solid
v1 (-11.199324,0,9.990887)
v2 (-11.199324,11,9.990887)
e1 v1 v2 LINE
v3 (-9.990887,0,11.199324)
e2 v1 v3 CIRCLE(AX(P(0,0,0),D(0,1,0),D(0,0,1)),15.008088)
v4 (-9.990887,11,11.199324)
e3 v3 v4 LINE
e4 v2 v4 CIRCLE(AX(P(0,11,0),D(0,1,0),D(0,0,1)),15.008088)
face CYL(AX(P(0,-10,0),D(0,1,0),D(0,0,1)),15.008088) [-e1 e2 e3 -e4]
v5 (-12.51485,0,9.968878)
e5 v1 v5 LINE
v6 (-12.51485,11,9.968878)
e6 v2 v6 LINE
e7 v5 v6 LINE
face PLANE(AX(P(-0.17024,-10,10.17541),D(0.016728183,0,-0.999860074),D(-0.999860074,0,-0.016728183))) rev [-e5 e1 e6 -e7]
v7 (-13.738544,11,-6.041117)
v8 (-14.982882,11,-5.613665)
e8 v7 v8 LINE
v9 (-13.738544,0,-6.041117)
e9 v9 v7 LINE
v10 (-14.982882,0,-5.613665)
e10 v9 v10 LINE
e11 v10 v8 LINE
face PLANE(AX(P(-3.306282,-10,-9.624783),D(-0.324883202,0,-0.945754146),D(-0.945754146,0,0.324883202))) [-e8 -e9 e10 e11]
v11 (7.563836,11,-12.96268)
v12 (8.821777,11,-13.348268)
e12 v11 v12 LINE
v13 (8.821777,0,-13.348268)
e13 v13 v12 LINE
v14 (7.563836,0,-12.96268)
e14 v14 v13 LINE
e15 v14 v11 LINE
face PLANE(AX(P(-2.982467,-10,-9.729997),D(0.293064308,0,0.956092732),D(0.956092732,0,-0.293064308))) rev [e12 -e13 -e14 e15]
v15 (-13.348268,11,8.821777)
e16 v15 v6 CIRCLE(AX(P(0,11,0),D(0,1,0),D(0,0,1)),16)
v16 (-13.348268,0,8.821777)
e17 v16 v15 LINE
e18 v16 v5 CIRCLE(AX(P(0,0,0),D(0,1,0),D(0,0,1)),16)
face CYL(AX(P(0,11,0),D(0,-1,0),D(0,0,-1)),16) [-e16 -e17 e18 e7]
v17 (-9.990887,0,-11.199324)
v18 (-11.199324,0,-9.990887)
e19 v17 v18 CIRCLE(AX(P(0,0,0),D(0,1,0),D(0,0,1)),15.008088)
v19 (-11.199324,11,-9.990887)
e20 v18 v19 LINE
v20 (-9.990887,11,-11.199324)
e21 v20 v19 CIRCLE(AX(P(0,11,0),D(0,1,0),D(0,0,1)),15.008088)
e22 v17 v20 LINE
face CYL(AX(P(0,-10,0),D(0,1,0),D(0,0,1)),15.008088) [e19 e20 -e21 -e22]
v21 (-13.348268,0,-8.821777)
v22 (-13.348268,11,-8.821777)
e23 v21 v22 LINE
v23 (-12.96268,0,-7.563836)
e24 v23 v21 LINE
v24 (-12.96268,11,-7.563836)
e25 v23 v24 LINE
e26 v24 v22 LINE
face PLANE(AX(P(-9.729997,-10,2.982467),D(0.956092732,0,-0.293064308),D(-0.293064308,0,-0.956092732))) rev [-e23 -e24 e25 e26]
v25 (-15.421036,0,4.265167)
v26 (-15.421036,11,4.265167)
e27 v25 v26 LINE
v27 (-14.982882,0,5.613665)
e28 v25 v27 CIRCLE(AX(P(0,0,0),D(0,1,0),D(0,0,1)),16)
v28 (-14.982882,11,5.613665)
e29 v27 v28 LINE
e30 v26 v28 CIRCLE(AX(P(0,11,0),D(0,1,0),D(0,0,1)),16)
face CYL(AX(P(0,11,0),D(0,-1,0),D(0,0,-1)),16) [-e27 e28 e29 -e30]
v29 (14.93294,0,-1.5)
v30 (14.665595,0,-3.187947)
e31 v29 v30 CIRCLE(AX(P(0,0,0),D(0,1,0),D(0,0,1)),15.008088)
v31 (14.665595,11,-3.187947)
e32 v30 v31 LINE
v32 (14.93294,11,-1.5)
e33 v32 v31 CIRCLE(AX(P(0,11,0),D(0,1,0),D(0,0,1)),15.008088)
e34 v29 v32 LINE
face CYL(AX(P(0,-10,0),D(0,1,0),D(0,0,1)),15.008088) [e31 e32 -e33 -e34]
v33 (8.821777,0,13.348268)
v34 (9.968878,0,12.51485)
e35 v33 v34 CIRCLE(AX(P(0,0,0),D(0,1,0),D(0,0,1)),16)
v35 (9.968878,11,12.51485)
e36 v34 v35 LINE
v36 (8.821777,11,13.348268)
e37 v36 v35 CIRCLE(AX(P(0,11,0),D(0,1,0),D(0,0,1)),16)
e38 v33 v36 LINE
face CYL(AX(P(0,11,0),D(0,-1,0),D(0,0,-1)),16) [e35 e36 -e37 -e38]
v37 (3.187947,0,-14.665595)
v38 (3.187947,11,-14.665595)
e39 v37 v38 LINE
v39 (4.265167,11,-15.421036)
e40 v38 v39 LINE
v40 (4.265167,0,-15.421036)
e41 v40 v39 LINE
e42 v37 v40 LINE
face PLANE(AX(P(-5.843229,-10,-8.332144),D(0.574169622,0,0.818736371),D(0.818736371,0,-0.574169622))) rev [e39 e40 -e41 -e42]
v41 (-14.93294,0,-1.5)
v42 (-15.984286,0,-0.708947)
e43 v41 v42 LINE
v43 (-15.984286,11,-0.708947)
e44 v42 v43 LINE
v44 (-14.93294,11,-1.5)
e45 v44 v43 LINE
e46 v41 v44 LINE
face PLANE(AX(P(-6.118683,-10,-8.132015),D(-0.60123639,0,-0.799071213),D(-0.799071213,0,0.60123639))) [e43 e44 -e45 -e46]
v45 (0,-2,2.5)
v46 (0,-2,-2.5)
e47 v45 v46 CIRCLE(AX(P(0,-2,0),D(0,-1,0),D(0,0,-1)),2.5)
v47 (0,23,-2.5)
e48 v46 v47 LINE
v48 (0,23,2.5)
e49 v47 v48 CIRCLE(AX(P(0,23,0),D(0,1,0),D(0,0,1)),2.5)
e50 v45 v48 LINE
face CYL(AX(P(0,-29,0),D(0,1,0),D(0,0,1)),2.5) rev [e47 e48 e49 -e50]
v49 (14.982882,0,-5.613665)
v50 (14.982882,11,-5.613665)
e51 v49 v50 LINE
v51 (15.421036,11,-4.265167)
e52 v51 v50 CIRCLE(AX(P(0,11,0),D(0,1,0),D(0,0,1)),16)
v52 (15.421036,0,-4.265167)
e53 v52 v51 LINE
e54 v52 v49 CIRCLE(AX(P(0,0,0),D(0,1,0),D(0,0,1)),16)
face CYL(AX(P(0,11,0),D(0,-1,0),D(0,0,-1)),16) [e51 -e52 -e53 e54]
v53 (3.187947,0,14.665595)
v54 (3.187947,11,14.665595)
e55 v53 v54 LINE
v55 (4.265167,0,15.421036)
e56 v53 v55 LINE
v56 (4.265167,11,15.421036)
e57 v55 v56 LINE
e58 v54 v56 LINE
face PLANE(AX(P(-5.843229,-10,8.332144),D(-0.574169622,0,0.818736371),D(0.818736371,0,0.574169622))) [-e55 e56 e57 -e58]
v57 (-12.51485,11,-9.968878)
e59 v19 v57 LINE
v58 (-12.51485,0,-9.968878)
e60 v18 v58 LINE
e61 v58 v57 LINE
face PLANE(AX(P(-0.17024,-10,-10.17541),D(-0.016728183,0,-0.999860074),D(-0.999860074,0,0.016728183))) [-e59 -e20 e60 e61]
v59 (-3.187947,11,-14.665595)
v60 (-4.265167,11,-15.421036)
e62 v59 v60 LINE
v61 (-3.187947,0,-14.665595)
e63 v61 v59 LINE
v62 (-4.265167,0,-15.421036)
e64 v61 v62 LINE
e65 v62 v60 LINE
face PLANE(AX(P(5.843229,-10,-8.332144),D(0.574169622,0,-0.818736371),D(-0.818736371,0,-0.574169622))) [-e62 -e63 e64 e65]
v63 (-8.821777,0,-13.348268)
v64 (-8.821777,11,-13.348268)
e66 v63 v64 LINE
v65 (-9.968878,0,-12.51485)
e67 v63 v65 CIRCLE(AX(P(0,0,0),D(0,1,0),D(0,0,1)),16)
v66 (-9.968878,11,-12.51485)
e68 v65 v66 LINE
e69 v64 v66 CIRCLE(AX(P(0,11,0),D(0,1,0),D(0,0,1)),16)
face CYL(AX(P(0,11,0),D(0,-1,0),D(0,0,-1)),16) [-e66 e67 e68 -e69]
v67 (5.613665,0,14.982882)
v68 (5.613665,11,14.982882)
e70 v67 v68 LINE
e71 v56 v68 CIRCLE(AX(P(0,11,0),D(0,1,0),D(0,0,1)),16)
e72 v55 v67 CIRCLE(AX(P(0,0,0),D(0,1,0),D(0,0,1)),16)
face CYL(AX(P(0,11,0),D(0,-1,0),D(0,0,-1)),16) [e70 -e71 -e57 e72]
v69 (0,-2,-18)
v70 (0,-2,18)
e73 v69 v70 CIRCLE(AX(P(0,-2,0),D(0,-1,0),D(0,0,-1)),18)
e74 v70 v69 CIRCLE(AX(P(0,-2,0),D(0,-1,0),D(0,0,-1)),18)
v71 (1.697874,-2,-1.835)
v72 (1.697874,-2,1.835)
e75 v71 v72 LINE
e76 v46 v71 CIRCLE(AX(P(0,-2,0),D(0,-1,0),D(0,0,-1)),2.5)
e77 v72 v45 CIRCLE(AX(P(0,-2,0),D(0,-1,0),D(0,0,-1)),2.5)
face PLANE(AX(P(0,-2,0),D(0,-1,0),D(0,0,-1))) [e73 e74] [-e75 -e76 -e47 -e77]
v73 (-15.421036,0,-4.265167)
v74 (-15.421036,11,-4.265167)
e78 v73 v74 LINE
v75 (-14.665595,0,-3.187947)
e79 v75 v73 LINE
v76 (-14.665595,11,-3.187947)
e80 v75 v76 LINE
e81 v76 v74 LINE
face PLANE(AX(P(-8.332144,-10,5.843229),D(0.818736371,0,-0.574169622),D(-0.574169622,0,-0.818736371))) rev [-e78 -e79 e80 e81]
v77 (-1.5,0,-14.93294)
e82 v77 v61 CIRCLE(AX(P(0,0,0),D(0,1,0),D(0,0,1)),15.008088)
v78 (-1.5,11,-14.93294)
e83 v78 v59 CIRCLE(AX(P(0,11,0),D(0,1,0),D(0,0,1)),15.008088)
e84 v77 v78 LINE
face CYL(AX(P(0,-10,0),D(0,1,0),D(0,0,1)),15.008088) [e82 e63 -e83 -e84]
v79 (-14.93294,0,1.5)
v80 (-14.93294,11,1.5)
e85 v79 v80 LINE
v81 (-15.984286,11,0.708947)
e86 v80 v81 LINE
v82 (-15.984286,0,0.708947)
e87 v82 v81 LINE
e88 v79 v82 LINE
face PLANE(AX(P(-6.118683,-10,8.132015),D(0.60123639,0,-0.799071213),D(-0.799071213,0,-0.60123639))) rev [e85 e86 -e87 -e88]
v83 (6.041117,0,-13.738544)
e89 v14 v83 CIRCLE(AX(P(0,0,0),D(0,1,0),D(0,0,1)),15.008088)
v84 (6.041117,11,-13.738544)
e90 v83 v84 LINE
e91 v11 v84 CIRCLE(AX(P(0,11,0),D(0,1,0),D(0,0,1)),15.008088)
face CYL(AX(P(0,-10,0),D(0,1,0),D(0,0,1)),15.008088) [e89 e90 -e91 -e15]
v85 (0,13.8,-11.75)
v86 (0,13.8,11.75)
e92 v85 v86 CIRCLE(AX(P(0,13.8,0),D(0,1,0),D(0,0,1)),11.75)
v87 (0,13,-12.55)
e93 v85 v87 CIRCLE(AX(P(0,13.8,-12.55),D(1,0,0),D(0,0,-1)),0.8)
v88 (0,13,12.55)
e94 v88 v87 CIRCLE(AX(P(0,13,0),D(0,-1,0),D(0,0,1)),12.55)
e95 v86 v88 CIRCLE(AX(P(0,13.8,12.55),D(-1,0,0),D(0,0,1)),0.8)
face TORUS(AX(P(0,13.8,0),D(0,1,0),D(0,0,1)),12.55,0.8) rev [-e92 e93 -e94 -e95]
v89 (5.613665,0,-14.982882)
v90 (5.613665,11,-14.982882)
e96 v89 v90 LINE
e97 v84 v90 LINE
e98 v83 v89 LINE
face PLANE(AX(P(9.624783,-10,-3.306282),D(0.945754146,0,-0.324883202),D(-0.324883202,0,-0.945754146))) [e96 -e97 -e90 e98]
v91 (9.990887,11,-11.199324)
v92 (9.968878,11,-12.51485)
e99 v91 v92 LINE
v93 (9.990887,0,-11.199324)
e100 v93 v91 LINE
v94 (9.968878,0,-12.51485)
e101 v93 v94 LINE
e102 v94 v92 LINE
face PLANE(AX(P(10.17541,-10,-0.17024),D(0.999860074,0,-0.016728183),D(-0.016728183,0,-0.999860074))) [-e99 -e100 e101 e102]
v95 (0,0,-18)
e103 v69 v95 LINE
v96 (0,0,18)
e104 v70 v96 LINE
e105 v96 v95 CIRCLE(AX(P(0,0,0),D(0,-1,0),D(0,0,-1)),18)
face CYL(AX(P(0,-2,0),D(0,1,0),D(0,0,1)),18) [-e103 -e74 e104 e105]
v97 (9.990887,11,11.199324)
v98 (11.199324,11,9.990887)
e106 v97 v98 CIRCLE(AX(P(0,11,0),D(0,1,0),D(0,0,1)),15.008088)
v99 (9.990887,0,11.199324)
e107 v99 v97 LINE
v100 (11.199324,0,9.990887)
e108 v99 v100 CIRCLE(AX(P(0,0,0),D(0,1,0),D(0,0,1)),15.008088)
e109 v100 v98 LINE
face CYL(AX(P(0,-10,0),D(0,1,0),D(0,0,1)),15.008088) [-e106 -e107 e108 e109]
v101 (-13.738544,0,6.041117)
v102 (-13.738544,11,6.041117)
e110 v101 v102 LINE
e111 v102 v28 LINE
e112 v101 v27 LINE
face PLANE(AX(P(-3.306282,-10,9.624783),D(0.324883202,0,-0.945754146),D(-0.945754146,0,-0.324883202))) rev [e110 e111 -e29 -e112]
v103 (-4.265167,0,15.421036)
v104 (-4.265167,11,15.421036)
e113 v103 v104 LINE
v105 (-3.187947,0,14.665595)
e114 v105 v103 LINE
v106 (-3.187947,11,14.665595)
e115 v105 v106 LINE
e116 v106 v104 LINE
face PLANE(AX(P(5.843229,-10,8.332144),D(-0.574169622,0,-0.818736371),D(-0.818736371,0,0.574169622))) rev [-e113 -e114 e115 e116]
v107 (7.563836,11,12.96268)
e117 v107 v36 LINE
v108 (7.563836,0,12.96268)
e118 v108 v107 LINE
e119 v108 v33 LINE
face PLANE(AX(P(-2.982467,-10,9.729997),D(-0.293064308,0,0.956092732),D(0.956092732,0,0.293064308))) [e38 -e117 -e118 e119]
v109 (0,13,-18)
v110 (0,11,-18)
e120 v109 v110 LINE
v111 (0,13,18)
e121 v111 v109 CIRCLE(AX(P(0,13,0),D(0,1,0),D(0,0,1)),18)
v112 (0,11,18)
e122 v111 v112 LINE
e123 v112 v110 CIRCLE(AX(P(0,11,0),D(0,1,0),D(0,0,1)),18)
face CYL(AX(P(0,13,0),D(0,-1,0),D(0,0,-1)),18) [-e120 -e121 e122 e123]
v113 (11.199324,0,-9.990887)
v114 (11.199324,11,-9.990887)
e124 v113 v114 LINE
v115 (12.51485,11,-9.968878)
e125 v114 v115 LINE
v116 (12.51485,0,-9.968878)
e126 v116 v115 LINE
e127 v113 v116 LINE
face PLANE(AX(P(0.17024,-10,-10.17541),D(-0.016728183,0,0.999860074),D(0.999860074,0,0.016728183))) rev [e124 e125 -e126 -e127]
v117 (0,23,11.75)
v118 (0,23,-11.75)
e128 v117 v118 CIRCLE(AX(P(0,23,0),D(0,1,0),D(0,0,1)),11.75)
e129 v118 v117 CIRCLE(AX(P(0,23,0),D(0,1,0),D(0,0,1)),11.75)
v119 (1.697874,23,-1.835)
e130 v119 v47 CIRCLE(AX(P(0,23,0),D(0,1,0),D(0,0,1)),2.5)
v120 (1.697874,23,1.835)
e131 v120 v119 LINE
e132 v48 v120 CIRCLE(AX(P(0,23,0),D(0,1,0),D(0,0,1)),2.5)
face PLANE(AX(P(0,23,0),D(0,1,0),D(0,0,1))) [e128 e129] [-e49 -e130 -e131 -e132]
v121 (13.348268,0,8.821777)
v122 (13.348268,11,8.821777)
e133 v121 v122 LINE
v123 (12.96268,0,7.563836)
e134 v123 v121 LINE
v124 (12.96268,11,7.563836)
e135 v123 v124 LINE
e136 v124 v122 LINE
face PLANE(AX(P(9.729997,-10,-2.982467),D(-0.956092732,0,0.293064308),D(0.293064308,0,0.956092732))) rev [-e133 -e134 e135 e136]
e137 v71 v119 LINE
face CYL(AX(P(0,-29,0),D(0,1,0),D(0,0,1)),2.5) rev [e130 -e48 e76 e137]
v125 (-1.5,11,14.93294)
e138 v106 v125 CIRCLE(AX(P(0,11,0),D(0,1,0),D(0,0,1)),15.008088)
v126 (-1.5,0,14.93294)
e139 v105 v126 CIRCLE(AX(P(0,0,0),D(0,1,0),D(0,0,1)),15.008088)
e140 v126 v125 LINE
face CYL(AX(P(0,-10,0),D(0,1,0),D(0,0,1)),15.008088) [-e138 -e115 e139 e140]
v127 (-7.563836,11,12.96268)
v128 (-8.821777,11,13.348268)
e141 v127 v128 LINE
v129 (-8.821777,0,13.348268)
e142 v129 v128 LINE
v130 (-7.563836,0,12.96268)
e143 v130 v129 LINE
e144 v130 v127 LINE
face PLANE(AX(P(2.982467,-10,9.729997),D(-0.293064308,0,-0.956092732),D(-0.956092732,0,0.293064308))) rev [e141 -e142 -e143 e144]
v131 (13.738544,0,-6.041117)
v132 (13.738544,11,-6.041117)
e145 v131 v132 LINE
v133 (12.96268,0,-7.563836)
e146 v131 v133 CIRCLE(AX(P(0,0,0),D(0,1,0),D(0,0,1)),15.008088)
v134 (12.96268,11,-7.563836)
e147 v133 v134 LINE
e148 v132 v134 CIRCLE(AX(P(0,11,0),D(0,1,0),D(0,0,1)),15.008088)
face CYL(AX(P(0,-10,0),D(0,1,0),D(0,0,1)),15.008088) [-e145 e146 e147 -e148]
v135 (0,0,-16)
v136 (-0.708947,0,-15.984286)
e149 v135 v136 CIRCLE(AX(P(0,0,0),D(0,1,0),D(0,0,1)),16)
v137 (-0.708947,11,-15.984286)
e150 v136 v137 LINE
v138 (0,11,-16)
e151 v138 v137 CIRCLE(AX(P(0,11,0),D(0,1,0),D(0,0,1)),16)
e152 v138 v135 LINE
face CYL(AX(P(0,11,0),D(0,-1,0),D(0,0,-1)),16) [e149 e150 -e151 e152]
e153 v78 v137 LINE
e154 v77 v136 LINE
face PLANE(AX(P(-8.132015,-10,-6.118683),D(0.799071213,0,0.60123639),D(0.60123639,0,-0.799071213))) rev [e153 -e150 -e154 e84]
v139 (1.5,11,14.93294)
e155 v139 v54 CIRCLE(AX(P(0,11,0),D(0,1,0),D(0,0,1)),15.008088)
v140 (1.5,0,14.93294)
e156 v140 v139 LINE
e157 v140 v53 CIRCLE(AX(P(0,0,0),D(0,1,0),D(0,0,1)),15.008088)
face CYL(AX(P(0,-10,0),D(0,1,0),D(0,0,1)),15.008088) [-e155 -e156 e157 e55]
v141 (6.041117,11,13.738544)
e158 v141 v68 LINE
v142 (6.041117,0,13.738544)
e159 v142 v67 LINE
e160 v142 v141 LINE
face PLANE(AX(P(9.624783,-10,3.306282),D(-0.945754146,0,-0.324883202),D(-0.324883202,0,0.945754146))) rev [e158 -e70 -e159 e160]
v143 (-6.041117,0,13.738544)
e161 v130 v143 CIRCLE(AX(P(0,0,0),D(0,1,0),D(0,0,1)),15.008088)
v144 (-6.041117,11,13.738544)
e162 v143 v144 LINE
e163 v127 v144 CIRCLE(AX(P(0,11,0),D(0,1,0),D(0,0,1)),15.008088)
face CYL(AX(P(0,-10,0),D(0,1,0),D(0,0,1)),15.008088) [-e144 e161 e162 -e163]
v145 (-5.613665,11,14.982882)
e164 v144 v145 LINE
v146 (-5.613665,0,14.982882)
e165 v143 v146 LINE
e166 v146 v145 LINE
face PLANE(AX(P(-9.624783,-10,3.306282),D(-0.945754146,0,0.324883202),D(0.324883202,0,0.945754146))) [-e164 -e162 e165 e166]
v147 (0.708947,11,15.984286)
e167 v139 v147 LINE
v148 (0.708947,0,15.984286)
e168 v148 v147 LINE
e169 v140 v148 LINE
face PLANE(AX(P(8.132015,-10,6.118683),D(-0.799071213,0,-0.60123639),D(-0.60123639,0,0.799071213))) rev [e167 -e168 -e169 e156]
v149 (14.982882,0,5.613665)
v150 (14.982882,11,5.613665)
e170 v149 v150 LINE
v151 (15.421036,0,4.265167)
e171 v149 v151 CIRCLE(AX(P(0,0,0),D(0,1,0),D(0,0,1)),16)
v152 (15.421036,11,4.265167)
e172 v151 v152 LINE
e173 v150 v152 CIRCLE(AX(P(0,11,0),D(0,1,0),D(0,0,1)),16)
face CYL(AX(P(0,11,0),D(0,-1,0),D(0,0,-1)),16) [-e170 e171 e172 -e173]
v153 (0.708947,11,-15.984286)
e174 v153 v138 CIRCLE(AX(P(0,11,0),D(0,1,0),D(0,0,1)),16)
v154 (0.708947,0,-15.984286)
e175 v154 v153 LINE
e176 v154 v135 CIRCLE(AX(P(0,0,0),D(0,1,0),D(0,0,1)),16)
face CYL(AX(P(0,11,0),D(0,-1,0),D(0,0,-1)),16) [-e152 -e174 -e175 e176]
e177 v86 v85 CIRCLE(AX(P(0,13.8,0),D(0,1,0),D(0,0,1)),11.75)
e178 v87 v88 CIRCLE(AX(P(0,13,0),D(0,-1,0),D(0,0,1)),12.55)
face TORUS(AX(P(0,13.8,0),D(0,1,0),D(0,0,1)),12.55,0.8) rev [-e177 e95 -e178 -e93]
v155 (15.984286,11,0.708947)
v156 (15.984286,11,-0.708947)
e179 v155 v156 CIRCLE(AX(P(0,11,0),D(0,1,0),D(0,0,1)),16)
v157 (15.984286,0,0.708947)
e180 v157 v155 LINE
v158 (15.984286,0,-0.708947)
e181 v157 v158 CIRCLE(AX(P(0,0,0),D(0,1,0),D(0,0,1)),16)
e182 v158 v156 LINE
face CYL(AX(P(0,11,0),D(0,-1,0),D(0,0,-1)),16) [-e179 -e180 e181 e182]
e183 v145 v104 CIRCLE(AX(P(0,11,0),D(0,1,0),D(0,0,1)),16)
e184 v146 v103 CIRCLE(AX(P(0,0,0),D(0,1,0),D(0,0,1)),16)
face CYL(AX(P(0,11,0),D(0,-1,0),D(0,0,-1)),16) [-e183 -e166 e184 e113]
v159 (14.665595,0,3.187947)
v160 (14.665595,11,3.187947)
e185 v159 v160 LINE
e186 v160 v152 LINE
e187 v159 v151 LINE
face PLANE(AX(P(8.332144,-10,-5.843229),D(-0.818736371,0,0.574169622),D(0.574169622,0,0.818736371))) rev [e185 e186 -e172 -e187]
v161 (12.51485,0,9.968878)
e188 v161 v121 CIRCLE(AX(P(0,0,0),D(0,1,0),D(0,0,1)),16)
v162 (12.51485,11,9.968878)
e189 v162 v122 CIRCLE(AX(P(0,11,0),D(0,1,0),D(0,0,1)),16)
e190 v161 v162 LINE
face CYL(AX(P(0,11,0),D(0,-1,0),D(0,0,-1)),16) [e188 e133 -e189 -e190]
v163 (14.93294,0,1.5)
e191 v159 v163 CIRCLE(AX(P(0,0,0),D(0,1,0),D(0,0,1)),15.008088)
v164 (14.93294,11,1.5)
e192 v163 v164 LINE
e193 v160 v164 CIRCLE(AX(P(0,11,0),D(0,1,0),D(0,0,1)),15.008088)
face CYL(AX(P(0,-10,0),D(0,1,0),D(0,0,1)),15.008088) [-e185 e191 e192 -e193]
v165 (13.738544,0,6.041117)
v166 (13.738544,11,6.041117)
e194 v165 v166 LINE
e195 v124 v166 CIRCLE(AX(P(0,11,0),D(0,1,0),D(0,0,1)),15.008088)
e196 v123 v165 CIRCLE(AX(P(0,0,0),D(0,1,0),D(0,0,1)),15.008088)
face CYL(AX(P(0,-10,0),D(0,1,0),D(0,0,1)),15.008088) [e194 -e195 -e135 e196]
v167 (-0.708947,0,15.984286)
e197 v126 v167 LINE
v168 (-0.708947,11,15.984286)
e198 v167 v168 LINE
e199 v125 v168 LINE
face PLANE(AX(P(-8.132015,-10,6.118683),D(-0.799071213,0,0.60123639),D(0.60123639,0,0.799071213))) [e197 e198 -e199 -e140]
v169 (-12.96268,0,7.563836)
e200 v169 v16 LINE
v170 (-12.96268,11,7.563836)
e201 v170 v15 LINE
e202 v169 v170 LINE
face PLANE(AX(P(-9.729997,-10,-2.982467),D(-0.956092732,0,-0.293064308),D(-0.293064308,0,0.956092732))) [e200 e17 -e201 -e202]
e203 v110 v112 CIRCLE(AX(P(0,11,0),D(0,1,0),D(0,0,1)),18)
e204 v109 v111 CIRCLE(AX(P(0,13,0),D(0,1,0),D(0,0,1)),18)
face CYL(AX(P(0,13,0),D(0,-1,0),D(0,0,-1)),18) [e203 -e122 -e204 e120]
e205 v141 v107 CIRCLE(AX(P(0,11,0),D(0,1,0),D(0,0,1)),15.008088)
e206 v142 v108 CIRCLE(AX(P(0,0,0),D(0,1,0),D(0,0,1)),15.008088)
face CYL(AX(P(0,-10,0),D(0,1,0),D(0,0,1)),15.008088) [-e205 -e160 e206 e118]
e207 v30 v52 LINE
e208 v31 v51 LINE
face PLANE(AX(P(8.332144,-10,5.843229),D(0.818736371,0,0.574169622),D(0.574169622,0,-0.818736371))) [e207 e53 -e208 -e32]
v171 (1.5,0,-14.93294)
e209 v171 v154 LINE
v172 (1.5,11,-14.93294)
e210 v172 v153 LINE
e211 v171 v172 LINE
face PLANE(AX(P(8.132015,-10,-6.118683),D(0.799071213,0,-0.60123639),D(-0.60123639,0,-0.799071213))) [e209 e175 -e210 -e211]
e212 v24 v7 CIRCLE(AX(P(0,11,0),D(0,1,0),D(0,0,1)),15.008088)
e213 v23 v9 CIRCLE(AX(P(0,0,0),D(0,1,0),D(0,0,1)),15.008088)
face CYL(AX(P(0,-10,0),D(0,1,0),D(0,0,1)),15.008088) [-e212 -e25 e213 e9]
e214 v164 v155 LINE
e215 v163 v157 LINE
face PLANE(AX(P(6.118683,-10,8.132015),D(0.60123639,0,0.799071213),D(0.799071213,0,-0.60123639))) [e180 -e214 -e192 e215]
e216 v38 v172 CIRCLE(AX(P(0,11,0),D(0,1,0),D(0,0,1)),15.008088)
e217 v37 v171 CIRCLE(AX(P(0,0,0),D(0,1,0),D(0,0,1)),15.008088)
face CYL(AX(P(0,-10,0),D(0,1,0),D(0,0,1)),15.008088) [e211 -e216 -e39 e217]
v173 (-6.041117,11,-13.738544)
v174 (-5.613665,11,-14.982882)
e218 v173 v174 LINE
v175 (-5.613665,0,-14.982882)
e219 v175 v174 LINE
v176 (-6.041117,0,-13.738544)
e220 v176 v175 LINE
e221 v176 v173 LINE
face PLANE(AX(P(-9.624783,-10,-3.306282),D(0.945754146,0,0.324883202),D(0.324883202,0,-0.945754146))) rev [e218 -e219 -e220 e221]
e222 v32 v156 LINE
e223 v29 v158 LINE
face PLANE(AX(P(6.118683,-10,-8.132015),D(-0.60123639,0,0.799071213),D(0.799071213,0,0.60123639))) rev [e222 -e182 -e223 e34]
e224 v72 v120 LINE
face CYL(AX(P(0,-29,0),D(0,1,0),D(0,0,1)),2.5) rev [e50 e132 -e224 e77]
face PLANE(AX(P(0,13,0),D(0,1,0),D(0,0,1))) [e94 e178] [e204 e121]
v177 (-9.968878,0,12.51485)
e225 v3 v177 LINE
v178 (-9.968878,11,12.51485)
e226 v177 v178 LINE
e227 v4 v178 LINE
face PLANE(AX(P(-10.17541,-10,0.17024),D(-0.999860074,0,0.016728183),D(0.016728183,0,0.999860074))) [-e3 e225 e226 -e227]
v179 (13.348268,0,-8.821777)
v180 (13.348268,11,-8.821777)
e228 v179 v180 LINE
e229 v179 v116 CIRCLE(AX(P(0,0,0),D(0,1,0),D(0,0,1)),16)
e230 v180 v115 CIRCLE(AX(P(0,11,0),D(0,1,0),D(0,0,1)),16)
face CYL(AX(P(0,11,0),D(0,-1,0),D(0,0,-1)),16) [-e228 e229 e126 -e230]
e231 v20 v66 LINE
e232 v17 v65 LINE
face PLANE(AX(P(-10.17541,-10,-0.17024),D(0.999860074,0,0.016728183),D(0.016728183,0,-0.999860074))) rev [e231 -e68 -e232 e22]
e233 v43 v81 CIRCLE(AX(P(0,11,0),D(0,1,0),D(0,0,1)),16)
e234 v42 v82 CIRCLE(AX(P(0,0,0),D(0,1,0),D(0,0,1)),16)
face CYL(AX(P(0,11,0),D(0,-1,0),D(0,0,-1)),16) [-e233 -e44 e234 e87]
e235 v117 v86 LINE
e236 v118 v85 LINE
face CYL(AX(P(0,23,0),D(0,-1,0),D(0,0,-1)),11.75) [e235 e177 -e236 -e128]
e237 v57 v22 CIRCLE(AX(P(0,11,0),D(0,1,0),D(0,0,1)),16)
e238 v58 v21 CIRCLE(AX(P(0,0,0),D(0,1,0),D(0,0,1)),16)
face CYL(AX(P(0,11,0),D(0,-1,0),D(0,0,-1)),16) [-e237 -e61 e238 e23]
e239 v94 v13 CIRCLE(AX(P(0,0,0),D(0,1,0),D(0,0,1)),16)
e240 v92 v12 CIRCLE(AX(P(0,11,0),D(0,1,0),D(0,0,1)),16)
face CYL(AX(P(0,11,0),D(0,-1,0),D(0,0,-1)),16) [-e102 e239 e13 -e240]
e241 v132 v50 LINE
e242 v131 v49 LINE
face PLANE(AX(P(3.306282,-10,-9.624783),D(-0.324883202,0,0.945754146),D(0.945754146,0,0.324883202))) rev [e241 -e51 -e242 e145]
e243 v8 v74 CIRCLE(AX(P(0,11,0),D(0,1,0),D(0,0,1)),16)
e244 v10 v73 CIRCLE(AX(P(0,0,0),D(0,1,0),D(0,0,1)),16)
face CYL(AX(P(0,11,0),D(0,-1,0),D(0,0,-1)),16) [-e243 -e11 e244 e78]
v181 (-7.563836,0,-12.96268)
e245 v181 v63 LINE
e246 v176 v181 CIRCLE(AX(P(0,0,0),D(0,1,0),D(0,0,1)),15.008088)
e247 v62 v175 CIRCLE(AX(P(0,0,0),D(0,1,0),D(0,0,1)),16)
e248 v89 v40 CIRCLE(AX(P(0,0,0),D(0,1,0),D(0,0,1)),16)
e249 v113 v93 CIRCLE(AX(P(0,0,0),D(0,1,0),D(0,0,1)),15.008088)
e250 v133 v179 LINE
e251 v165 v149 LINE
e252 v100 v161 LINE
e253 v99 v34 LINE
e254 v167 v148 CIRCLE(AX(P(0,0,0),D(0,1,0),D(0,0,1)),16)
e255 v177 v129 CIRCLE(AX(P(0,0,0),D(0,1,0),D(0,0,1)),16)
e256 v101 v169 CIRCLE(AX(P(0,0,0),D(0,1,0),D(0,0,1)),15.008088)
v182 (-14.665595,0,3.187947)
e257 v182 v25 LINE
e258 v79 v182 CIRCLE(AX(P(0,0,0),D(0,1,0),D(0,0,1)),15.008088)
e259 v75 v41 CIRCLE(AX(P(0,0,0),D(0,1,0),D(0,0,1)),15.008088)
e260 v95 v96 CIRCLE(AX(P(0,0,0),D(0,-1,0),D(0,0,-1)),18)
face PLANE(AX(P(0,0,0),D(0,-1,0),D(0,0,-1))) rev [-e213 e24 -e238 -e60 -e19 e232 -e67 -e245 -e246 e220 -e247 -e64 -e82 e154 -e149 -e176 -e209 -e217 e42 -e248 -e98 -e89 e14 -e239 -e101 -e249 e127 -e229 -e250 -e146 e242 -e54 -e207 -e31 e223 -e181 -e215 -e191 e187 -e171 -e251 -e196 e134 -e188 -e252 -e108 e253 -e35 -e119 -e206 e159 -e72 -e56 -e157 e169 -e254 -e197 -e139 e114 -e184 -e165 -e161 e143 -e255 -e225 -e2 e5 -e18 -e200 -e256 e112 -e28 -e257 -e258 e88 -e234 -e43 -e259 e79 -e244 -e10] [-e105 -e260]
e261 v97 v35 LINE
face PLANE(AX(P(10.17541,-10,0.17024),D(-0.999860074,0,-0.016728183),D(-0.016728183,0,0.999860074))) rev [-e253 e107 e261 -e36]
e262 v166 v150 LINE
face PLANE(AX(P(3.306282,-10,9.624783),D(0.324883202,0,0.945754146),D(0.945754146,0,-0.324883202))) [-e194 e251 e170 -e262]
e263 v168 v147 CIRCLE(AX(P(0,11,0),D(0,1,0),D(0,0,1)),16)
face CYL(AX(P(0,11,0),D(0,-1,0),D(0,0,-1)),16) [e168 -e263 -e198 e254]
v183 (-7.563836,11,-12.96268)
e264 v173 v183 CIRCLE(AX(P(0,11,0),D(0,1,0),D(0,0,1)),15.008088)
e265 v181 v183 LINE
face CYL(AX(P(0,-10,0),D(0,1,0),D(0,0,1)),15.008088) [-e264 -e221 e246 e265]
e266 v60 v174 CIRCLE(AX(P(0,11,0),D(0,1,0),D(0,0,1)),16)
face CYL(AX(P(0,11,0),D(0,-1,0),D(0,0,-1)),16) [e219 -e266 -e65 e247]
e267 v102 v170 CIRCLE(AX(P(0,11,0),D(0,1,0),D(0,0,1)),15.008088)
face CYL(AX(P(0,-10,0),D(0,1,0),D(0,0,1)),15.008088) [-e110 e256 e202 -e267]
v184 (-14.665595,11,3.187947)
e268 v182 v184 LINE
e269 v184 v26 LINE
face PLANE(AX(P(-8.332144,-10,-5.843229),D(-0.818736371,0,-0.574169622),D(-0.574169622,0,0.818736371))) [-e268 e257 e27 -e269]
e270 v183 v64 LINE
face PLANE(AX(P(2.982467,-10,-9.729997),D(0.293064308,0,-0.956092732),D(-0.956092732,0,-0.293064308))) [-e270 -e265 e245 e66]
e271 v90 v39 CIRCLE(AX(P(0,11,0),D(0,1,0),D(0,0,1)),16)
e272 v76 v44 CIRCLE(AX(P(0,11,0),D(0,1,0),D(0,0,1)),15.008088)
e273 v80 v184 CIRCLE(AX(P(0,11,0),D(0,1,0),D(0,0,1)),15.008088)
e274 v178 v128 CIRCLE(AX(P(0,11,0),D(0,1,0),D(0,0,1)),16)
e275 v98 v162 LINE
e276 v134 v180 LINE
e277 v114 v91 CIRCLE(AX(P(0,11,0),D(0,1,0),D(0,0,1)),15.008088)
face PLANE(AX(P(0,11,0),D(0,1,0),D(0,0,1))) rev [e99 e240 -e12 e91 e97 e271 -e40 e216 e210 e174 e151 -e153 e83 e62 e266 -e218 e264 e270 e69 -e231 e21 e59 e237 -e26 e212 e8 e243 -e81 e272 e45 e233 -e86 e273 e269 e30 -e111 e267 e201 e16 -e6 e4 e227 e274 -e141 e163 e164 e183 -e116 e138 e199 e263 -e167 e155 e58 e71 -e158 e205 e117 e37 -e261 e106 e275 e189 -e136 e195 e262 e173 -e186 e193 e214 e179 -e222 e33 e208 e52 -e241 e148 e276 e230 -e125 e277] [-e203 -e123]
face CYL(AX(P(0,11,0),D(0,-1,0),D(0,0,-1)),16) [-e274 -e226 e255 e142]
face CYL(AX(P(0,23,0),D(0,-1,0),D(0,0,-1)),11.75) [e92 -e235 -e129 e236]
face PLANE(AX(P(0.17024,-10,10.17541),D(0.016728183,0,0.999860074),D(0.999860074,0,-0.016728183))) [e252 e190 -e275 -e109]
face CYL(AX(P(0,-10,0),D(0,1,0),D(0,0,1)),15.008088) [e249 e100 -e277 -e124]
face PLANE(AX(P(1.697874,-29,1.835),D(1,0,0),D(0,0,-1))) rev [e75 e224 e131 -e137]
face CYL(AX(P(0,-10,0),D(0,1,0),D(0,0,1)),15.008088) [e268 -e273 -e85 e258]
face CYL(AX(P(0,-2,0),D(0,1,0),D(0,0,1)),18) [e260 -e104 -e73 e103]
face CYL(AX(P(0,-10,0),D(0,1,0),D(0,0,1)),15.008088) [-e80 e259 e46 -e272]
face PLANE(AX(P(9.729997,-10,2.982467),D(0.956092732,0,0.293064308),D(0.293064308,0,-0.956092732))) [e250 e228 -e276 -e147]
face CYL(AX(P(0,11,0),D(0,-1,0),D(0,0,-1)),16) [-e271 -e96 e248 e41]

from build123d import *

# Parameters (mm, degrees)
SKETCH1_R           = 16
BOSS_EXTRUDE1_DEPTH = 11
CUT_EXTRUDE2_START  = -21
CUT_EXTRUDE2_DEPTH  = 21
SKETCH3_R           = 18
BOSS_EXTRUDE2_DEPTH = 2
BOSS_EXTRUDE3_START = 2
SKETCH4_R           = 18
BOSS_EXTRUDE3_DEPTH = 2
SKETCH5_R           = 11.75
BOSS_EXTRUDE4_DEPTH = 10
FILLET1_R           = 0.8
CUT_EXTRUDE3_DEPTH  = 52


with BuildPart() as part:
    # Sketch1 → Boss-Extrude1 (new body)
    with BuildSketch(Plane(origin=(0, 0, 0), x_dir=(1, 0, 0), z_dir=(0, 1, 0))):
        with Locations(Location((0, 0, 0), (0, 0, 270))):
            Circle(SKETCH1_R)
    extrude(amount=BOSS_EXTRUDE1_DEPTH)

    # Sketch2 → Cut-Extrude2 (cut)
    with BuildSketch(Plane(origin=(0, 11, 0), x_dir=(1, 0, 0), z_dir=(0, 1, 0)).offset(CUT_EXTRUDE2_START)):
        with BuildLine():
            ThreePointArc((4.265167024, 15.421035966), (2.502951441, 15.80301345), (0.708947293, 15.984285838))
            Line((0.708947293, 15.984285838), (1.5, 14.932939883))
            ThreePointArc((1.5, 14.932939883), (2.347782156, 14.823313142), (3.187947426, 14.665595275))
            Line((3.187947426, 14.665595275), (4.265167024, 15.421035966))
        make_face()
        with BuildLine():
            ThreePointArc((8.821777076, 13.348267649), (7.263847996, 14.256104387), (5.613664909, 14.982882443))
            Line((5.613664909, 14.982882443), (6.041116974, 13.738544292))
            ThreePointArc((6.041116974, 13.738544292), (6.813529192, 13.372303972), (7.563836345, 12.96268002))
            Line((7.563836345, 12.96268002), (8.821777076, 13.348267649))
        make_face()
        with BuildLine():
            ThreePointArc((12.514850122, 9.968877892), (11.313708499, 11.313708499), (9.968877892, 12.514850122))
            Line((9.968877892, 12.514850122), (9.990887328, 11.199324263))
            ThreePointArc((9.990887328, 11.199324263), (10.612320518, 10.612320518), (11.199324263, 9.990887328))
            Line((11.199324263, 9.990887328), (12.514850122, 9.968877892))
        make_face()
        with BuildLine():
            ThreePointArc((14.982882443, 5.613664909), (14.256104387, 7.263847996), (13.348267649, 8.821777076))
            Line((13.348267649, 8.821777076), (12.96268002, 7.563836345))
            ThreePointArc((12.96268002, 7.563836345), (13.372303972, 6.813529192), (13.738544292, 6.041116974))
            Line((13.738544292, 6.041116974), (14.982882443, 5.613664909))
        make_face()
        with BuildLine():
            ThreePointArc((15.984285838, 0.708947293), (15.80301345, 2.502951441), (15.421035966, 4.265167024))
            Line((15.421035966, 4.265167024), (14.665595275, 3.187947426))
            ThreePointArc((14.665595275, 3.187947426), (14.823313142, 2.347782156), (14.932939883, 1.5))
            Line((14.932939883, 1.5), (15.984285838, 0.708947293))
        make_face()
        with BuildLine():
            ThreePointArc((15.421035966, -4.265167024), (15.80301345, -2.502951441), (15.984285838, -0.708947293))
            Line((15.984285838, -0.708947293), (14.932939883, -1.5))
            ThreePointArc((14.932939883, -1.5), (14.823313142, -2.347782156), (14.665595275, -3.187947426))
            Line((14.665595275, -3.187947426), (15.421035966, -4.265167024))
        make_face()
        with BuildLine():
            ThreePointArc((13.348267649, -8.821777076), (14.256104387, -7.263847996), (14.982882443, -5.613664909))
            Line((14.982882443, -5.613664909), (13.738544292, -6.041116974))
            ThreePointArc((13.738544292, -6.041116974), (13.372303972, -6.813529192), (12.96268002, -7.563836345))
            Line((12.96268002, -7.563836345), (13.348267649, -8.821777076))
        make_face()
        with BuildLine():
            ThreePointArc((9.968877892, -12.514850122), (11.313708499, -11.313708499), (12.514850122, -9.968877892))
            Line((12.514850122, -9.968877892), (11.199324263, -9.990887328))
            ThreePointArc((11.199324263, -9.990887328), (10.612320518, -10.612320518), (9.990887328, -11.199324263))
            Line((9.990887328, -11.199324263), (9.968877892, -12.514850122))
        make_face()
        with BuildLine():
            ThreePointArc((5.613664909, -14.982882443), (7.263847996, -14.256104387), (8.821777076, -13.348267649))
            Line((8.821777076, -13.348267649), (7.563836345, -12.96268002))
            ThreePointArc((7.563836345, -12.96268002), (6.813529192, -13.372303972), (6.041116974, -13.738544292))
            Line((6.041116974, -13.738544292), (5.613664909, -14.982882443))
        make_face()
        with BuildLine():
            Line((1.5, -14.932939883), (0.708947293, -15.984285838))
            ThreePointArc((0.708947293, -15.984285838), (2.502951441, -15.80301345), (4.265167024, -15.421035966))
            Line((4.265167024, -15.421035966), (3.187947426, -14.665595275))
            ThreePointArc((3.187947426, -14.665595275), (2.347782156, -14.823313142), (1.5, -14.932939883))
        make_face()
        with BuildLine():
            Line((-3.187947426, -14.665595275), (-4.265167024, -15.421035966))
            ThreePointArc((-4.265167024, -15.421035966), (-2.502951441, -15.80301345), (-0.708947293, -15.984285838))
            Line((-0.708947293, -15.984285838), (-1.5, -14.932939883))
            ThreePointArc((-1.5, -14.932939883), (-2.347782156, -14.823313142), (-3.187947426, -14.665595275))
        make_face()
        with BuildLine():
            Line((-7.563836345, -12.96268002), (-8.821777076, -13.348267649))
            ThreePointArc((-8.821777076, -13.348267649), (-7.263847996, -14.256104387), (-5.613664909, -14.982882443))
            Line((-5.613664909, -14.982882443), (-6.041116974, -13.738544292))
            ThreePointArc((-6.041116974, -13.738544292), (-6.813529192, -13.372303972), (-7.563836345, -12.96268002))
        make_face()
        with BuildLine():
            Line((-11.199324263, -9.990887328), (-12.514850122, -9.968877892))
            ThreePointArc((-12.514850122, -9.968877892), (-11.313708499, -11.313708499), (-9.968877892, -12.514850122))
            Line((-9.968877892, -12.514850122), (-9.990887328, -11.199324263))
            ThreePointArc((-9.990887328, -11.199324263), (-10.612320518, -10.612320518), (-11.199324263, -9.990887328))
        make_face()
        with BuildLine():
            Line((-13.738544292, -6.041116974), (-14.982882443, -5.613664909))
            ThreePointArc((-14.982882443, -5.613664909), (-14.256104387, -7.263847996), (-13.348267649, -8.821777076))
            Line((-13.348267649, -8.821777076), (-12.96268002, -7.563836345))
            ThreePointArc((-12.96268002, -7.563836345), (-13.372303972, -6.813529192), (-13.738544292, -6.041116974))
        make_face()
        with BuildLine():
            Line((-14.932939883, -1.5), (-15.984285838, -0.708947293))
            ThreePointArc((-15.984285838, -0.708947293), (-15.80301345, -2.502951441), (-15.421035966, -4.265167024))
            Line((-15.421035966, -4.265167024), (-14.665595275, -3.187947426))
            ThreePointArc((-14.665595275, -3.187947426), (-14.823313142, -2.347782156), (-14.932939883, -1.5))
        make_face()
        with BuildLine():
            Line((-14.665595275, 3.187947426), (-15.421035966, 4.265167024))
            ThreePointArc((-15.421035966, 4.265167024), (-15.80301345, 2.502951441), (-15.984285838, 0.708947293))
            Line((-15.984285838, 0.708947293), (-14.932939883, 1.5))
            ThreePointArc((-14.932939883, 1.5), (-14.823313142, 2.347782156), (-14.665595275, 3.187947426))
        make_face()
        with BuildLine():
            Line((-12.96268002, 7.563836345), (-13.348267649, 8.821777076))
            ThreePointArc((-13.348267649, 8.821777076), (-14.256104387, 7.263847996), (-14.982882443, 5.613664909))
            Line((-14.982882443, 5.613664909), (-13.738544292, 6.041116974))
            ThreePointArc((-13.738544292, 6.041116974), (-13.372303972, 6.813529192), (-12.96268002, 7.563836345))
        make_face()
        with BuildLine():
            Line((-9.990887328, 11.199324263), (-9.968877892, 12.514850122))
            ThreePointArc((-9.968877892, 12.514850122), (-11.313708499, 11.313708499), (-12.514850122, 9.968877892))
            Line((-12.514850122, 9.968877892), (-11.199324263, 9.990887328))
            ThreePointArc((-11.199324263, 9.990887328), (-10.612320518, 10.612320518), (-9.990887328, 11.199324263))
        make_face()
        with BuildLine():
            Line((-6.041116974, 13.738544292), (-5.613664909, 14.982882443))
            ThreePointArc((-5.613664909, 14.982882443), (-7.263847996, 14.256104387), (-8.821777076, 13.348267649))
            Line((-8.821777076, 13.348267649), (-7.563836345, 12.96268002))
            ThreePointArc((-7.563836345, 12.96268002), (-6.813529192, 13.372303972), (-6.041116974, 13.738544292))
        make_face()
        with BuildLine():
            ThreePointArc((-3.187947426, 14.665595275), (-2.347782156, 14.823313142), (-1.5, 14.932939883))
            Line((-1.5, 14.932939883), (-0.708947293, 15.984285838))
            ThreePointArc((-0.708947293, 15.984285838), (-2.502951441, 15.80301345), (-4.265167024, 15.421035966))
            Line((-4.265167024, 15.421035966), (-3.187947426, 14.665595275))
        make_face()
    extrude(amount=CUT_EXTRUDE2_DEPTH, mode=Mode.SUBTRACT)

    # Sketch3 → Boss-Extrude2 (add)
    with BuildSketch(Plane(origin=(0, 11, 0), x_dir=(1, 0, 0), z_dir=(0, 1, 0))):
        with Locations(Location((0, 0, 0), (0, 0, 270))):
            Circle(SKETCH3_R)
    extrude(amount=BOSS_EXTRUDE2_DEPTH)

    # Sketch4 → Boss-Extrude3 (add)
    with BuildSketch(Plane.XZ.offset(BOSS_EXTRUDE3_START)):
        with Locations(Location((0, 0, 0), (0, 0, 90))):
            Circle(SKETCH4_R)
    extrude(amount=-BOSS_EXTRUDE3_DEPTH)

    # Sketch5 → Boss-Extrude4 (add)
    with BuildSketch(Plane(origin=(0, 13, 0), x_dir=(1, 0, 0), z_dir=(0, 1, 0))):
        with Locations(Location((0, 0, 0), (0, 0, 270))):
            Circle(SKETCH5_R)
    extrude(amount=BOSS_EXTRUDE4_DEPTH)

    # Fillet1
    fillet1_edges = [part.edges().sort_by_distance(p)[0] for p in [
        (0, 13, -11.75),
    ]]
    fillet(fillet1_edges, radius=FILLET1_R)

    # Sketch6 → Cut-Extrude3 (cut)
    with BuildSketch(Plane(origin=(0, 23, 0), x_dir=(1, 0, 0), z_dir=(0, 1, 0))):
        with BuildLine():
            Line((1.69787367, -1.835), (1.69787367, 1.835))
            ThreePointArc((1.69787367, 1.835), (-2.5, 0), (1.69787367, -1.835))
        make_face()
    extrude(amount=-CUT_EXTRUDE3_DEPTH, mode=Mode.SUBTRACT)


solid = part.part
